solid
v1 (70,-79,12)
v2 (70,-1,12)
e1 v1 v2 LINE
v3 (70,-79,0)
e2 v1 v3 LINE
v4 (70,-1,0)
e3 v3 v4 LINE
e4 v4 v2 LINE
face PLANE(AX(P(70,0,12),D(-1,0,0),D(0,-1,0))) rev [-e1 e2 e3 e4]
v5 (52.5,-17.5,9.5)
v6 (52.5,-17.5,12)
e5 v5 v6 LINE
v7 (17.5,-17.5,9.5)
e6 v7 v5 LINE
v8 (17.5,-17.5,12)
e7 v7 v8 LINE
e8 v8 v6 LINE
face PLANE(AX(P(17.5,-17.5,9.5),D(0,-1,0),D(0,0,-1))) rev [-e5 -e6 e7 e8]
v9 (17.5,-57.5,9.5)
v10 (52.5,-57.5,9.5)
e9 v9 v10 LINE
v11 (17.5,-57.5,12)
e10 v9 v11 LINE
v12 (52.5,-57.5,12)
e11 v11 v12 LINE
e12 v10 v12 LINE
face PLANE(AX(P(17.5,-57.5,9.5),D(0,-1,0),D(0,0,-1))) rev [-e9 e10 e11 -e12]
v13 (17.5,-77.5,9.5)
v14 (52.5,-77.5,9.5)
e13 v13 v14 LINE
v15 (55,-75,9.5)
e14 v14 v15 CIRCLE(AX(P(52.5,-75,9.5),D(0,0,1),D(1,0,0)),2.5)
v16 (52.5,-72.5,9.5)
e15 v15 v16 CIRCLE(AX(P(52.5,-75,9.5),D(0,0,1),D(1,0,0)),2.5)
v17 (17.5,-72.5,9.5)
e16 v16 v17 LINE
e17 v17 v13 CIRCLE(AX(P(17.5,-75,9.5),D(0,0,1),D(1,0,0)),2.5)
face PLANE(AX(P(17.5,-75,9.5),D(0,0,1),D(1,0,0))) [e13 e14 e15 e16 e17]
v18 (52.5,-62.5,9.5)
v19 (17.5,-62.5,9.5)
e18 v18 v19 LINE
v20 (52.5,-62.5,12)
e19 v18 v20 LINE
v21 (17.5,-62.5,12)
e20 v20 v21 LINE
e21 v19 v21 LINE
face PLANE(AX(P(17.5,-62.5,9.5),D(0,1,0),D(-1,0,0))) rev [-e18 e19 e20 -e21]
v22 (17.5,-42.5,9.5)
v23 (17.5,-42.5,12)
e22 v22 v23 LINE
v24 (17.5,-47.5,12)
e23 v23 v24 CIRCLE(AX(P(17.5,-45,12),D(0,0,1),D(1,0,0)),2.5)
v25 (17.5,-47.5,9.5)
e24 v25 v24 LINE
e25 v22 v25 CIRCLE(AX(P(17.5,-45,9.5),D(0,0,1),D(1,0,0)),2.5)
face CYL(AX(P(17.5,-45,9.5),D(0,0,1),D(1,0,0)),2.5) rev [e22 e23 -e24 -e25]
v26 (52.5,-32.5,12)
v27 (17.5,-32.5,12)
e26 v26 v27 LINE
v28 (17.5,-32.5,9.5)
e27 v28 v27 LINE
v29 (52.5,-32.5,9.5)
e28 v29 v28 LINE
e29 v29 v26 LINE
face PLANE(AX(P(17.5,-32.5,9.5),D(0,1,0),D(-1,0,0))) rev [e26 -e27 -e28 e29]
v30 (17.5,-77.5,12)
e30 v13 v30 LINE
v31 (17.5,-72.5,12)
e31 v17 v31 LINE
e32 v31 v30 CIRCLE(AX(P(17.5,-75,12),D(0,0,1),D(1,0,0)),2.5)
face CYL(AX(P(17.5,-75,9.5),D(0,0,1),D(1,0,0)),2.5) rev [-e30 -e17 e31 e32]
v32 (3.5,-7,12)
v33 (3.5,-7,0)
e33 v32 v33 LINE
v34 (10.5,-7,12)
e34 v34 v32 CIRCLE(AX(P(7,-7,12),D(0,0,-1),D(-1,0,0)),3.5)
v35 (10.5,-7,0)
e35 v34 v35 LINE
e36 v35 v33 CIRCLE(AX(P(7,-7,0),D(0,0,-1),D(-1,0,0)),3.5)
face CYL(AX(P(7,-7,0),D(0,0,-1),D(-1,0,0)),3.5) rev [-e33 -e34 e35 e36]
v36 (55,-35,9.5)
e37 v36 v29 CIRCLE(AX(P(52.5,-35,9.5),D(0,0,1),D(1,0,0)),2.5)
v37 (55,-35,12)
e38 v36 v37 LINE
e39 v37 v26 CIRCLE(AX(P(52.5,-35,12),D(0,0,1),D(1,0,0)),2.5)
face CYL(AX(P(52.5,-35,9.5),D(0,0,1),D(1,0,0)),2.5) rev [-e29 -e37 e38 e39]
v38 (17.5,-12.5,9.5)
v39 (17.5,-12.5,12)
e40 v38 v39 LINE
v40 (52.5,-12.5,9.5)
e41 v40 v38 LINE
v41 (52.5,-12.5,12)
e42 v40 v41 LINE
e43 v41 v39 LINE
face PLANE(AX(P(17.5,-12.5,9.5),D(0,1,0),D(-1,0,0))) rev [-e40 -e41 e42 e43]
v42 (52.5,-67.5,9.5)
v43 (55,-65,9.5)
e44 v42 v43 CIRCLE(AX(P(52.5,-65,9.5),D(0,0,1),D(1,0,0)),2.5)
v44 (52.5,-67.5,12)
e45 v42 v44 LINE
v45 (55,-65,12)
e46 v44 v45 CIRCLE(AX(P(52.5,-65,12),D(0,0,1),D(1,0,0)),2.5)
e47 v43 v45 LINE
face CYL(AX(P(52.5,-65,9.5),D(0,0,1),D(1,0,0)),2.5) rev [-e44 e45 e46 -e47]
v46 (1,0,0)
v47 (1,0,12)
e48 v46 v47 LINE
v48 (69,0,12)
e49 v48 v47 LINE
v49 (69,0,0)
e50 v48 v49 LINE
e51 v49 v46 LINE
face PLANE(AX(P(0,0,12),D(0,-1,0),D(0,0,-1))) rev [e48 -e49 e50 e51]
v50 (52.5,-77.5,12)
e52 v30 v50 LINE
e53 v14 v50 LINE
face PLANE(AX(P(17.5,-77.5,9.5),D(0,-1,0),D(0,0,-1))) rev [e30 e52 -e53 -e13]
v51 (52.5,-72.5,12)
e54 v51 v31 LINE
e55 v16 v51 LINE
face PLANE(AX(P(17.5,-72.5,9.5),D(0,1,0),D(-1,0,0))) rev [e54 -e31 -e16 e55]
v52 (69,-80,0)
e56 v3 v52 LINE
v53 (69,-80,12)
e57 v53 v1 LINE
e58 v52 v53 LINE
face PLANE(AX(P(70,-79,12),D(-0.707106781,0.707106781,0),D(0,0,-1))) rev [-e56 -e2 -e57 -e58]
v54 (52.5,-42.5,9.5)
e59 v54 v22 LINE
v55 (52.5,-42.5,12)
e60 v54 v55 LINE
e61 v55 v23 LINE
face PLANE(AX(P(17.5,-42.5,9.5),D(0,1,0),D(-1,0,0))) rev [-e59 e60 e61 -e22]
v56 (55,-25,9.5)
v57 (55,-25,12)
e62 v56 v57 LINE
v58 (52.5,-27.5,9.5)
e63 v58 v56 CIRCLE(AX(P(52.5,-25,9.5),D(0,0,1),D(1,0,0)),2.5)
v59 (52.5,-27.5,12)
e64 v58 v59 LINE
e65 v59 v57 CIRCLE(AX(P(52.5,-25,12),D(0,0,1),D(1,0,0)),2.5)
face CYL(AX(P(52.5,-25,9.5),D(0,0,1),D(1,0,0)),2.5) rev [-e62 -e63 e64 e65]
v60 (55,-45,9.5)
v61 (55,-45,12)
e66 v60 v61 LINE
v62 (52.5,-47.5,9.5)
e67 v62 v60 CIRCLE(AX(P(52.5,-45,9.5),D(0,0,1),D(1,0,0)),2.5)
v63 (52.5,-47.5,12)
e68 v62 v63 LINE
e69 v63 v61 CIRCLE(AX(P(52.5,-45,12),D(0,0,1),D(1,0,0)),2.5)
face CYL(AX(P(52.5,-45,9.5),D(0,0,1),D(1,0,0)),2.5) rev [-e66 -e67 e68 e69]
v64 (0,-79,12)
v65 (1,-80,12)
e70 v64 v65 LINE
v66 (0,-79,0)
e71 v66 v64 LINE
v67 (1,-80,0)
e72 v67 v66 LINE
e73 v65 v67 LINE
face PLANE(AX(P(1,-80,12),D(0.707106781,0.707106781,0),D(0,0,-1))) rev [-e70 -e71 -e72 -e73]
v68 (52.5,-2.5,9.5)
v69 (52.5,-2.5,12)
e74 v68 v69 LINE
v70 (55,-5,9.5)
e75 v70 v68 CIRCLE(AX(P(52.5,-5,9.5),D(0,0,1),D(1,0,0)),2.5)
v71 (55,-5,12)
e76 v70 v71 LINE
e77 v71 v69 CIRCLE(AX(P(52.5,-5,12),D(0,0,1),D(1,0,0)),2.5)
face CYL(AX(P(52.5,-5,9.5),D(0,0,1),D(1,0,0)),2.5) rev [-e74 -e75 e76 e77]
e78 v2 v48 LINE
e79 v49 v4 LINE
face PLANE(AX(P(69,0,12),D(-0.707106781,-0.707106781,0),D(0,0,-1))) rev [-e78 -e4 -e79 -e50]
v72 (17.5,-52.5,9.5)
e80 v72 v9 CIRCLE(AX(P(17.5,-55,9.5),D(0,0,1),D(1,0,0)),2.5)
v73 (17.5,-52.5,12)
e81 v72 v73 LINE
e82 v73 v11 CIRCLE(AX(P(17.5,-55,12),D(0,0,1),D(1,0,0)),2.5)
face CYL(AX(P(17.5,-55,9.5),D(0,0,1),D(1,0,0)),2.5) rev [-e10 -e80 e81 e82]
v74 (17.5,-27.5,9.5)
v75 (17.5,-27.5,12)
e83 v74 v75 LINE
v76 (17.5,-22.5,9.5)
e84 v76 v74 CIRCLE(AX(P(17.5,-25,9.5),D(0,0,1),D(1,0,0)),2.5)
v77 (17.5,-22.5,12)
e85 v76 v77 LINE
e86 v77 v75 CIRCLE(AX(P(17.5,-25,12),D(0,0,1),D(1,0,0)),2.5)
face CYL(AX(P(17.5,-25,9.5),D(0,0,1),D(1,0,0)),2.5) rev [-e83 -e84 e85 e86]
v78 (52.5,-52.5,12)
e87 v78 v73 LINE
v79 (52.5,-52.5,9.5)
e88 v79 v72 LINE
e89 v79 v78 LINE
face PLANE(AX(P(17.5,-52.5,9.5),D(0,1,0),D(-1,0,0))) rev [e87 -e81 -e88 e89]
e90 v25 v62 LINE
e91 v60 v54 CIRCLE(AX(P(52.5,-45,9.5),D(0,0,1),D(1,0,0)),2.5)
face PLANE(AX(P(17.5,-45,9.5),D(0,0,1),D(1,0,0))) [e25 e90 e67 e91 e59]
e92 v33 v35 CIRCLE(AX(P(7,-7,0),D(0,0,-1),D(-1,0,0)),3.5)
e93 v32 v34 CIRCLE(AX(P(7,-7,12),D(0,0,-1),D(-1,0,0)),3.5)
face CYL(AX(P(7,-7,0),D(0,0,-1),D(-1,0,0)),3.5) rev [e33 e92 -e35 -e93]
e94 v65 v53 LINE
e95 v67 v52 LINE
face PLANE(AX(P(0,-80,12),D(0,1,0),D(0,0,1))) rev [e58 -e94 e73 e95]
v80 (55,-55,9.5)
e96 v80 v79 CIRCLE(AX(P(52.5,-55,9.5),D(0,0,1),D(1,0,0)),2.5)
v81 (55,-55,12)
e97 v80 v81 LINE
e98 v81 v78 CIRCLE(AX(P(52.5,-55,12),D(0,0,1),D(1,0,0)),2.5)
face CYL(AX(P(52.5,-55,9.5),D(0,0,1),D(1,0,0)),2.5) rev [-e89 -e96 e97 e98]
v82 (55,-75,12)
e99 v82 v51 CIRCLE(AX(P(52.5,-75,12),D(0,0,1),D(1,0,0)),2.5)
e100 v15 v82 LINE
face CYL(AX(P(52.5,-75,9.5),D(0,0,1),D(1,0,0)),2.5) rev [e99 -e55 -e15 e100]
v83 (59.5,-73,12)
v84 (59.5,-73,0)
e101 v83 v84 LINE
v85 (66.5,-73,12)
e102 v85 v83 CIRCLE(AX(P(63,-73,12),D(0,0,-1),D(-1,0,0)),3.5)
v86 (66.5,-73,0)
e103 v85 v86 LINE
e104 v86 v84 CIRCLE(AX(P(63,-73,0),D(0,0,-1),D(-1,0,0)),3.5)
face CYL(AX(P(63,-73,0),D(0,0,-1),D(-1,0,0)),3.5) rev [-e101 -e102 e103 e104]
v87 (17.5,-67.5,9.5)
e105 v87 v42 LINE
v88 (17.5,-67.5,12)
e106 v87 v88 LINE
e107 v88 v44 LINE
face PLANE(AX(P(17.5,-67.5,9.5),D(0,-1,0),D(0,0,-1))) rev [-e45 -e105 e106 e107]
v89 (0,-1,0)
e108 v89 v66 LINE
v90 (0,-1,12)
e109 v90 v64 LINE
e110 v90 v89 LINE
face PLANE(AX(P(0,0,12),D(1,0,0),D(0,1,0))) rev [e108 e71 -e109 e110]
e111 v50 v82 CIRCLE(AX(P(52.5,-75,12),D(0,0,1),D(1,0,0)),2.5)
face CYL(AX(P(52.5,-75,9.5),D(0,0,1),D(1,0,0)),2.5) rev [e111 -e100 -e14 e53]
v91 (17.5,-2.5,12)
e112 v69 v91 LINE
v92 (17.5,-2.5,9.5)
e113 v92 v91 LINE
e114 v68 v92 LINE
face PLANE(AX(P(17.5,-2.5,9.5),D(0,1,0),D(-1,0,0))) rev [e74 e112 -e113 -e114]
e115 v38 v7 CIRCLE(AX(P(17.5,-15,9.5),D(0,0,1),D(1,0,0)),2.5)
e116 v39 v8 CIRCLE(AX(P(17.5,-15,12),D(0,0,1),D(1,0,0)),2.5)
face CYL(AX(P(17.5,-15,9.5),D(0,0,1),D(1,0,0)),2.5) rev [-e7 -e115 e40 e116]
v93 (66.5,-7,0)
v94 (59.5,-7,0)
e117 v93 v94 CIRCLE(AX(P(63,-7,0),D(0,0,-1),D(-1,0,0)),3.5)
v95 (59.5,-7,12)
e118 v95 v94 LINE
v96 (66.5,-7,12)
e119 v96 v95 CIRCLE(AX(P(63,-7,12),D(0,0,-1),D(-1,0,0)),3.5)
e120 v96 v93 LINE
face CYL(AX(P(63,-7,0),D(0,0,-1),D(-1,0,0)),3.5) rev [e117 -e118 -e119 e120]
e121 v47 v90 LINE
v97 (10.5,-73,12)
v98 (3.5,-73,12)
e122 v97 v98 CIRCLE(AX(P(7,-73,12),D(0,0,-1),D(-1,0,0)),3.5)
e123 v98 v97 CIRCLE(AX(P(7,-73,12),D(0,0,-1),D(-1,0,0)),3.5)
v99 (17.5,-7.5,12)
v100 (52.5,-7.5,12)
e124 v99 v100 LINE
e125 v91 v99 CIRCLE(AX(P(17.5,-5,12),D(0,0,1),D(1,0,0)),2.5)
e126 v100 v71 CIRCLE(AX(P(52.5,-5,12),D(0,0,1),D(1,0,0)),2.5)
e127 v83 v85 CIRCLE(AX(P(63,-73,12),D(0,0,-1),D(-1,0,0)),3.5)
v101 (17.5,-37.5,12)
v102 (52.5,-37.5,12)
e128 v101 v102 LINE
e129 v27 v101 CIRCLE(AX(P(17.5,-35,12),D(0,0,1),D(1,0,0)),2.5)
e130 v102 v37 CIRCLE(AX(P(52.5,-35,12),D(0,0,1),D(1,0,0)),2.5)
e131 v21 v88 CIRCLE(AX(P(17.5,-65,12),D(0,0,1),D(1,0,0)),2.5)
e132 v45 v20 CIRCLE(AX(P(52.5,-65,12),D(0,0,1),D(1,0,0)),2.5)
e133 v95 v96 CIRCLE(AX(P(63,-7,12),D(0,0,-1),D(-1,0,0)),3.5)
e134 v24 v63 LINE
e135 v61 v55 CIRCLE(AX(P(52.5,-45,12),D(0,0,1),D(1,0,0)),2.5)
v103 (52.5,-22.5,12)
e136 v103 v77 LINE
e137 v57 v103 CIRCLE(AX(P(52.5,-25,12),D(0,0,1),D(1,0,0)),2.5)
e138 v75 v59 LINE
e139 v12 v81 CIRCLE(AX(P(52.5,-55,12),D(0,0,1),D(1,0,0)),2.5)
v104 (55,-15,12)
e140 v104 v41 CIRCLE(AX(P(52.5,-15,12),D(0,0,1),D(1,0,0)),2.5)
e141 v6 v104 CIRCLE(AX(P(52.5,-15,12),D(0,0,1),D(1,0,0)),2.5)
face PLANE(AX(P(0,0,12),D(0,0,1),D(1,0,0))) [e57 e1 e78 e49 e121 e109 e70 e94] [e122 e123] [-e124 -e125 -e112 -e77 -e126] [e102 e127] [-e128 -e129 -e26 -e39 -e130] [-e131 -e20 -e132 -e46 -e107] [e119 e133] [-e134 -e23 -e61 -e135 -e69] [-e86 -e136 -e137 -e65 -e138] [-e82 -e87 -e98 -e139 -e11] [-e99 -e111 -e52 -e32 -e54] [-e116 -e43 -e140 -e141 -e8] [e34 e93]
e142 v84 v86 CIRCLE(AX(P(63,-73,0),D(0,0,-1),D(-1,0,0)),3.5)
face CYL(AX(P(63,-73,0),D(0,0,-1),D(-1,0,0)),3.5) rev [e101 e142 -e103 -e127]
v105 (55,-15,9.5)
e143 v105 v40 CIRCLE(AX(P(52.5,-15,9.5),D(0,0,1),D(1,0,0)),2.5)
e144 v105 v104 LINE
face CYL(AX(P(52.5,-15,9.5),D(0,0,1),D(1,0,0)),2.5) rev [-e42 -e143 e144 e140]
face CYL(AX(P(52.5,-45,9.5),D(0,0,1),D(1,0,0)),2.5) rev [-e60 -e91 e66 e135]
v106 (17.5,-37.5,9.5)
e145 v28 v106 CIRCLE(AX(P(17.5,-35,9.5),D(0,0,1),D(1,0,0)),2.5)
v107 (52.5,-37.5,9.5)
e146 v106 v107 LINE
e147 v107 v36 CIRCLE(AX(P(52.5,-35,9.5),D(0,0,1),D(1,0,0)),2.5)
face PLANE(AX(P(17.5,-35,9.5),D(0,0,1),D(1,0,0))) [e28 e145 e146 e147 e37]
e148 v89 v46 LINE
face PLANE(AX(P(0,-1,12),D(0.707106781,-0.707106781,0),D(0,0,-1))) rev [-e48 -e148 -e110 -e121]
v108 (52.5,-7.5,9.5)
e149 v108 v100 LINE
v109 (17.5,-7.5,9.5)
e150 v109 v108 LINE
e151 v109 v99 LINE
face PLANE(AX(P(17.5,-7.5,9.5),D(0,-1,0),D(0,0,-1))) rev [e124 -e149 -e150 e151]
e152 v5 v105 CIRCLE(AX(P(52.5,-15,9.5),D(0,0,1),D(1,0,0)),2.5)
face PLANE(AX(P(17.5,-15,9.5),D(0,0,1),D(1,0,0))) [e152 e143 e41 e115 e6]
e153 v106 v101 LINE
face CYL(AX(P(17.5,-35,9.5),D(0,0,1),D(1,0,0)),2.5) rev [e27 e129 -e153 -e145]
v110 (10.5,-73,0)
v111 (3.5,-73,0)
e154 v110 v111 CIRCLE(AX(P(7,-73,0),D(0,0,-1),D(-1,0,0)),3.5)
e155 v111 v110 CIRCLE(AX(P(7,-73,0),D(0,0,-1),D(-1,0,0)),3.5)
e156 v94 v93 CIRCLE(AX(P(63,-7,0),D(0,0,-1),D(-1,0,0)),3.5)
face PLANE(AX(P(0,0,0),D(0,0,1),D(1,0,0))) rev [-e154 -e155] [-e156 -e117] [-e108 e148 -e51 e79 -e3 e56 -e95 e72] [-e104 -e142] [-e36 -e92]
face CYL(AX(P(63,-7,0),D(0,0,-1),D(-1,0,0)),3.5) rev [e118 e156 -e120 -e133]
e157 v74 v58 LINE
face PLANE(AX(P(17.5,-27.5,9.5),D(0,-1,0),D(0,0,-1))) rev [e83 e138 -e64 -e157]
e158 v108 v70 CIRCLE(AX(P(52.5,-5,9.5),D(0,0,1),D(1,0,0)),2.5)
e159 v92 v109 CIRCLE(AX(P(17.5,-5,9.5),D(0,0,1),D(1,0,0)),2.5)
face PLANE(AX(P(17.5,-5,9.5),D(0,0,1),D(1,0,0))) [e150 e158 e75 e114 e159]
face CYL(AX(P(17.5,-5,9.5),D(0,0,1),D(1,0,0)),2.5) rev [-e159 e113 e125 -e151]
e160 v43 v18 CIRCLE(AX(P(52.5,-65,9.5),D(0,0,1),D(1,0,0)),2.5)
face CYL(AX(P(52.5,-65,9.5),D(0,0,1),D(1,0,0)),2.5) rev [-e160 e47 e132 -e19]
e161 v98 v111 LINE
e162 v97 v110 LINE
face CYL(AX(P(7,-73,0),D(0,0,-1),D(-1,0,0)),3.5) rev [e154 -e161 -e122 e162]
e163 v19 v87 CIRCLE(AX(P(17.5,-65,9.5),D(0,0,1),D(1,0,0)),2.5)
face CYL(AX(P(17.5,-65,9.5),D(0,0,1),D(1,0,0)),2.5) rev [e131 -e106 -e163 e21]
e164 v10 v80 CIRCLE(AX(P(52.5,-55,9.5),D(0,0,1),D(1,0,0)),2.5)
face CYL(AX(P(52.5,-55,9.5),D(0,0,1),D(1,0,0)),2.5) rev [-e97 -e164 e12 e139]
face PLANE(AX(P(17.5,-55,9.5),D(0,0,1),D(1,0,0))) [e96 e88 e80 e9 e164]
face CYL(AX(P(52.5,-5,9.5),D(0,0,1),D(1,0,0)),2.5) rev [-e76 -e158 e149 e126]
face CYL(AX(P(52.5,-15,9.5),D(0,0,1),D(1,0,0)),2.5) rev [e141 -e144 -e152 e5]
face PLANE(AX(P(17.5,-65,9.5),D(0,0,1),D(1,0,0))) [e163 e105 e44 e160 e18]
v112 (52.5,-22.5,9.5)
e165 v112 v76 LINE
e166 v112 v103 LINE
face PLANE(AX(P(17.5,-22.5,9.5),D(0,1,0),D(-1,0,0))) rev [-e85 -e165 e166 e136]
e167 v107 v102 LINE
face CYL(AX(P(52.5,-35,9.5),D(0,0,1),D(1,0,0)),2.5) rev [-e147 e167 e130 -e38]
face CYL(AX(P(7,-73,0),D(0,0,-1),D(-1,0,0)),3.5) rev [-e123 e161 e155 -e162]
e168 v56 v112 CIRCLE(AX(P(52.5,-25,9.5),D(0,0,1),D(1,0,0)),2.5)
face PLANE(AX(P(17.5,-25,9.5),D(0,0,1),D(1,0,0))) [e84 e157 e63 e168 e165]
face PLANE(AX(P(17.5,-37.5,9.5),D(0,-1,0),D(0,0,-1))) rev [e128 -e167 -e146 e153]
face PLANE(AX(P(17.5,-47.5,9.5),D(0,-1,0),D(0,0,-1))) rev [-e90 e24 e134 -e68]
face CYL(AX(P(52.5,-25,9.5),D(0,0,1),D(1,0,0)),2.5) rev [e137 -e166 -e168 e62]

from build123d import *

# Parameters (mm, degrees)
SKETCH_1_W             = 70
SKETCH_1_H             = 80
EXTRUDE_1_DEPTH        = 12
CHAMFER_1_SIZE         = 1
CUT_EXTRUDE_1_DEPTH    = 2.5
PATTERN_LINEAR_1_COUNT = 8
PATTERN_LINEAR_1_PITCH = 10
HOLE_WIZARD_7_0_7_1_D  = 7


with BuildPart() as part:
    # 草图1 → 凸台-拉伸1 (new body)
    with BuildSketch(Plane.XY):
        with Locations((35, -40)):
            Rectangle(SKETCH_1_W, SKETCH_1_H)
    extrude(amount=EXTRUDE_1_DEPTH)

    # 倒角1
    chamfer_1_edges = [part.edges().sort_by_distance(p)[0] for p in [
        (0, 0, 6),
        (70, 0, 6),
        (70, -80, 6),
        (0, -80, 6),
    ]]
    chamfer(chamfer_1_edges, length=CHAMFER_1_SIZE)

    # 草图2 → 切除-拉伸1 (cut)
    with BuildSketch(Plane.XY.offset(12)):
        with BuildLine():
            Line((17.5, -2.5), (52.5, -2.5))
            ThreePointArc((52.5, -2.5), (55, -5), (52.5, -7.5))
            Line((52.5, -7.5), (17.5, -7.5))
            ThreePointArc((17.5, -7.5), (15, -5), (17.5, -2.5))
        make_face()
    cut_extrude_1 = extrude(amount=-CUT_EXTRUDE_1_DEPTH, mode=Mode.SUBTRACT)

    # 阵列(线性)1: 切除-拉伸1 ×8
    with Locations(*[(0, -i * PATTERN_LINEAR_1_PITCH, 0) for i in range(1, PATTERN_LINEAR_1_COUNT)]):
        add(cut_extrude_1, mode=Mode.SUBTRACT)

    # Ø7.0 (7) 直径孔1 (through all)
    with Locations(Plane(origin=(0, 0, 0), x_dir=(-1, 0, 0), z_dir=(0, 0, -1))):
        with Locations((-7, -73), (-7, -7), (-63, -73), (-63, -7)):
            Hole(HOLE_WIZARD_7_0_7_1_D / 2)


solid = part.part
